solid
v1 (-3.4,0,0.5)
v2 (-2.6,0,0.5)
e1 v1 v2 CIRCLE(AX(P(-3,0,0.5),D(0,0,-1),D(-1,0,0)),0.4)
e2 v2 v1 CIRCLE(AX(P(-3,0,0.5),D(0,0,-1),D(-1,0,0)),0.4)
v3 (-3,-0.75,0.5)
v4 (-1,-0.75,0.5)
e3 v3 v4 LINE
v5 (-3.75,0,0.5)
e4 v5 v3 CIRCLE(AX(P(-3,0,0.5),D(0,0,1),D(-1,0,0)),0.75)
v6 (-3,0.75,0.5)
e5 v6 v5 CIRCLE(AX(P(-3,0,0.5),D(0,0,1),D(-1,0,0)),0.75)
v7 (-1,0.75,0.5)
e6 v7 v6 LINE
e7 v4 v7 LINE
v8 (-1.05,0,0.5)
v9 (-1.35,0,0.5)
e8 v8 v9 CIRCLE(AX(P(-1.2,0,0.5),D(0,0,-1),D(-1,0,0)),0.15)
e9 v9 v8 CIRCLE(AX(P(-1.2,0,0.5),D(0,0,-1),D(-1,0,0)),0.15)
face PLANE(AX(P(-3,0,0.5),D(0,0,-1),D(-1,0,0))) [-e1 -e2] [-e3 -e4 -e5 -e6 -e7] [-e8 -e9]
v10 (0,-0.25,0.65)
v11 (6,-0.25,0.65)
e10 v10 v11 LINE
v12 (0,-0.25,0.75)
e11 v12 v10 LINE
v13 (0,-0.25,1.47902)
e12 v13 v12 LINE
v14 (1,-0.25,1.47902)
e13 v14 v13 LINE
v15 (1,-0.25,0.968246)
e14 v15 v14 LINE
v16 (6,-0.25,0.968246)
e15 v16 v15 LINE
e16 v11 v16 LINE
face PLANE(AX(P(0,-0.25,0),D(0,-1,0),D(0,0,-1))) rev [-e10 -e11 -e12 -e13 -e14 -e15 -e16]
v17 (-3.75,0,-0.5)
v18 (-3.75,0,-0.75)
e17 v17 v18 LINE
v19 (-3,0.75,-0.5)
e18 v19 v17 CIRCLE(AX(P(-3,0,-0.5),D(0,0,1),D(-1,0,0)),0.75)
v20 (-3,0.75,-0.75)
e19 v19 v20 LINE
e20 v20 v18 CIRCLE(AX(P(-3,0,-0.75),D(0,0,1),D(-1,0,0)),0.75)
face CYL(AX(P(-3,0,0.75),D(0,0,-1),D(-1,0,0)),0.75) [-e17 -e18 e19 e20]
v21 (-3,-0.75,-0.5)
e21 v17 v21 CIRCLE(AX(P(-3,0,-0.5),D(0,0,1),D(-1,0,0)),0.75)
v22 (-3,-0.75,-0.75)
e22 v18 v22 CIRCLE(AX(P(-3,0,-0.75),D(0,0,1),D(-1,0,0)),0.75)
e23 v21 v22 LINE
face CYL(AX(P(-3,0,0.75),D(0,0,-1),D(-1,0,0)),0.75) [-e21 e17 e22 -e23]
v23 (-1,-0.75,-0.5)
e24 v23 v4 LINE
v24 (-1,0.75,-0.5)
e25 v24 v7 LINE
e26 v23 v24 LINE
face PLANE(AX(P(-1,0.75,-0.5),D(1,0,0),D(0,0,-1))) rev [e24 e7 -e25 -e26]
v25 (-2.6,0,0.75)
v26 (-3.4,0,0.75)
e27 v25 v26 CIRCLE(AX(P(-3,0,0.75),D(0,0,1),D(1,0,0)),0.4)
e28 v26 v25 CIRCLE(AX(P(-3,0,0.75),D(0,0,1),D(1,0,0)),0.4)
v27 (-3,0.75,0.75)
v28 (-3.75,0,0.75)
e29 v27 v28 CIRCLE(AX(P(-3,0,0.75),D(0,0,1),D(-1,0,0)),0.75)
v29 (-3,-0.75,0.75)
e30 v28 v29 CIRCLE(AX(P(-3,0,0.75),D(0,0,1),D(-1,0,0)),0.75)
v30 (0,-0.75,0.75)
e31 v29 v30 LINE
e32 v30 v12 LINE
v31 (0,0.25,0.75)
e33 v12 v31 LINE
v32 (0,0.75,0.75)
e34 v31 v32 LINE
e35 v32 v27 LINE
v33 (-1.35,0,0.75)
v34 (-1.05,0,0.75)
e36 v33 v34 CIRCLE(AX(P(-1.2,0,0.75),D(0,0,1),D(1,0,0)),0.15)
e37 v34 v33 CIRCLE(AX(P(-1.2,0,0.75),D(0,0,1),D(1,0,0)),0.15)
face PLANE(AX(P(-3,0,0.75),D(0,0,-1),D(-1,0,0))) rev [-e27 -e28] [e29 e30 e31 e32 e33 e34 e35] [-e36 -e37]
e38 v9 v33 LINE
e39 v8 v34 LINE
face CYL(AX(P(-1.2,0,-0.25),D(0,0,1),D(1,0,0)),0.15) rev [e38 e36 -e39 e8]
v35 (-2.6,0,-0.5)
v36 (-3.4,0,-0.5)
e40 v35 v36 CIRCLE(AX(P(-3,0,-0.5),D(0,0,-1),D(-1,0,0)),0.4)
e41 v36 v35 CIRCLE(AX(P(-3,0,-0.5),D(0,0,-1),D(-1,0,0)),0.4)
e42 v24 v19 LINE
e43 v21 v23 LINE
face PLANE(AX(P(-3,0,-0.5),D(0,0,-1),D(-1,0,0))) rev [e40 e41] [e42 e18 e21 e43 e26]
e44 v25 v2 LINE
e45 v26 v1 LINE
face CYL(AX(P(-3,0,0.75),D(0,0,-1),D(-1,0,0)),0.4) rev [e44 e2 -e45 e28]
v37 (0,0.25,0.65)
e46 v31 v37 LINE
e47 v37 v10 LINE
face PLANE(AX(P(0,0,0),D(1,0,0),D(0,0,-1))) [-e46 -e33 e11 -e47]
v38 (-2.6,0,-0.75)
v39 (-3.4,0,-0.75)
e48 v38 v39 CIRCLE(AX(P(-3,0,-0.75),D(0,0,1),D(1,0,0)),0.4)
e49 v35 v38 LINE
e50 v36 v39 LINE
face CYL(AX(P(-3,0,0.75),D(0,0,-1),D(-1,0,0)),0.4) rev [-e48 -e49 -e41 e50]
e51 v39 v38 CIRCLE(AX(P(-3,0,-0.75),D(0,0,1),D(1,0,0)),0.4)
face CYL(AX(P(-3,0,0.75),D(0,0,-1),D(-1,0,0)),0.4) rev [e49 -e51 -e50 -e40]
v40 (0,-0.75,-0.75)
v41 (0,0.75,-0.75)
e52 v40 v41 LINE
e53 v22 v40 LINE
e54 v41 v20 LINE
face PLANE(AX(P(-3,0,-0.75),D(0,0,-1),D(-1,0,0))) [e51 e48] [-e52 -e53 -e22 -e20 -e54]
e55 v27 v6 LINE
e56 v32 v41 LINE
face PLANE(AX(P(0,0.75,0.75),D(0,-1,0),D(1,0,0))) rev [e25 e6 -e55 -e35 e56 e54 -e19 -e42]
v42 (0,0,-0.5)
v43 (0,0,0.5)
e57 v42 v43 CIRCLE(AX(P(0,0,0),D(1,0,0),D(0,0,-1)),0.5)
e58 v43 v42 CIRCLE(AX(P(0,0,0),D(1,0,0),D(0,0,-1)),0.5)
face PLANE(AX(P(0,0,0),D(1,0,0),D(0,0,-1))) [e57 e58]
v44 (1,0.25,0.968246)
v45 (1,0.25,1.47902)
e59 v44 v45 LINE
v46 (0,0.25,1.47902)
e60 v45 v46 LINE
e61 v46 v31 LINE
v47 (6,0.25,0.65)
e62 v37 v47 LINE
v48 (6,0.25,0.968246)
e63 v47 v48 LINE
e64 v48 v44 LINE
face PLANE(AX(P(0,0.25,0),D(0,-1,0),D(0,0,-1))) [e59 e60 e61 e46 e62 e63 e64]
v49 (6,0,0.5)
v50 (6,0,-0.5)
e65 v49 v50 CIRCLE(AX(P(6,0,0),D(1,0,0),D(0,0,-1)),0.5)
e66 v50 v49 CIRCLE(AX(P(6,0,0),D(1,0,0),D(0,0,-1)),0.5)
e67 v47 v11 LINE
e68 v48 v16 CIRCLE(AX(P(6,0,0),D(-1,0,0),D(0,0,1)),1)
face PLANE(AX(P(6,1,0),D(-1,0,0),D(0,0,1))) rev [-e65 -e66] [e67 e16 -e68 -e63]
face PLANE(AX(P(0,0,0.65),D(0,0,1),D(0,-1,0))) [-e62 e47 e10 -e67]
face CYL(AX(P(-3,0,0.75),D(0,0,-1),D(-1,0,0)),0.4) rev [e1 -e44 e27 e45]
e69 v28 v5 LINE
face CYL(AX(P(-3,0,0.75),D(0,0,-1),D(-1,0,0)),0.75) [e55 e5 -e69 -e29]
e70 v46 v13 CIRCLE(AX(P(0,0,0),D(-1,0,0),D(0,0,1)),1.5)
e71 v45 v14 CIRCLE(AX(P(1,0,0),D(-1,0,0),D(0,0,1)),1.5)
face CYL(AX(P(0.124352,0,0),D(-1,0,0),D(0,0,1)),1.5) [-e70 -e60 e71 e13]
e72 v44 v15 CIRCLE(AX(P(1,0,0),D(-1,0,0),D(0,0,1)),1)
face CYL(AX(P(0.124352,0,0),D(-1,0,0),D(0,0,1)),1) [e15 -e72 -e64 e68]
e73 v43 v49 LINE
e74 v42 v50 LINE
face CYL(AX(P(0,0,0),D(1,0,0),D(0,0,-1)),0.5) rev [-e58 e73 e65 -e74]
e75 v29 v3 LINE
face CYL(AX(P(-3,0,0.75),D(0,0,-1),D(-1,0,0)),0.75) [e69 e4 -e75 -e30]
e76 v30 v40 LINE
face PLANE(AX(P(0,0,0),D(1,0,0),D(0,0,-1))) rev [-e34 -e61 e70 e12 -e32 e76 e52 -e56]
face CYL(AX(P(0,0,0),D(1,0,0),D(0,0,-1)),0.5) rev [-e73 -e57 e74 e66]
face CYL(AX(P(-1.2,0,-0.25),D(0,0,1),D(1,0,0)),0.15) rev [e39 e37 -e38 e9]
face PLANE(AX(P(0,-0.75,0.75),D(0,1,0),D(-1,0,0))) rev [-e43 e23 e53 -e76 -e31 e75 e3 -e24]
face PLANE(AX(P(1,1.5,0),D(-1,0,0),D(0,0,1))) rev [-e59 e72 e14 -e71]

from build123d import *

# Parameters (mm, degrees)
SKETCH2_R           = 0.4
BOSS_EXTRUDE1_DEPTH = 0.75
CUT_EXTRUDE1_DEPTH  = 0.5
SKETCH4_R           = 0.5
CUT_EXTRUDE2_DEPTH  = 6
CUT_EXTRUDE4_DEPTH  = 6
SKETCH6_R           = 0.15
CUT_EXTRUDE5_DEPTH  = 1


with BuildPart() as part:
    # Sketch1 → Revolve1 (revolve)
    with BuildSketch(Plane.XY, mode=Mode.PRIVATE) as revolve1_sk:
        Polygon((0, 0), (0, 1.5), (1, 1.5), (1, 1), (6, 1), (6, 0), align=None)
    revolve(revolve1_sk.sketch.rotate(Axis((0.124352332, 0, 0), (1, 0, 0)), 90), axis=Axis((0.124352332, 0, 0), (1, 0, 0)))

    # Sketch2 → Boss-Extrude1 (add, symmetric)
    with BuildSketch(Plane.XY):
        with BuildLine():
            Line((0, 0.75), (0, -0.75))
            Line((0, -0.75), (-3, -0.75))
            ThreePointArc((-3, -0.75), (-3.75, 0), (-3, 0.75))
            Line((-3, 0.75), (0, 0.75))
        make_face()
        with Locations((-3, 0)):
            Circle(SKETCH2_R, mode=Mode.SUBTRACT)
    extrude(amount=BOSS_EXTRUDE1_DEPTH, both=True)

    # Sketch3 → Cut-Extrude1 (cut, symmetric)
    with BuildSketch(Plane.XY):
        with BuildLine():
            Line((-1, 0.75), (-1, -0.75))
            Line((-1, -0.75), (-3, -0.75))
            ThreePointArc((-3, -0.75), (-3.75, 0), (-3, 0.75))
            Line((-3, 0.75), (-1, 0.75))
        make_face()
    extrude(amount=CUT_EXTRUDE1_DEPTH, both=True, mode=Mode.SUBTRACT)

    # Sketch4 → Cut-Extrude2 (cut)
    with BuildSketch(Plane(origin=(6, 0, 0), x_dir=(0, 0, -1), z_dir=(1, 0, 0))):
        Circle(SKETCH4_R)
    extrude(amount=-CUT_EXTRUDE2_DEPTH, mode=Mode.SUBTRACT)

    # Sketch5 → Cut-Extrude4 (cut)
    with BuildSketch(Plane(origin=(6, 0, 0), x_dir=(0, 0, -1), z_dir=(1, 0, 0))):
        with BuildLine():
            Line((-0.65, -0.25), (-0.65, 0.25))
            Line((-0.65, 0.25), (-0.968245837, 0.25))
            ThreePointArc((-0.968245837, 0.25), (-1, 0), (-0.968245837, -0.25))
            Line((-0.968245837, -0.25), (-0.65, -0.25))
        make_face()
        with BuildLine():
            ThreePointArc((-0.968245837, -0.25), (-1, 0), (-0.968245837, 0.25))
            Line((-0.968245837, 0.25), (-1.818815546, 0.25))
            Line((-1.818815546, 0.25), (-1.818815546, -0.25))
            Line((-1.818815546, -0.25), (-0.968245837, -0.25))
        make_face()
    extrude(amount=-CUT_EXTRUDE4_DEPTH, mode=Mode.SUBTRACT)

    # Sketch6 → Cut-Extrude5 (cut)
    with BuildSketch(Plane.XY.offset(0.75)):
        with Locations((-1.2, 0)):
            Circle(SKETCH6_R)
    extrude(amount=-CUT_EXTRUDE5_DEPTH, mode=Mode.SUBTRACT)


solid = part.part
